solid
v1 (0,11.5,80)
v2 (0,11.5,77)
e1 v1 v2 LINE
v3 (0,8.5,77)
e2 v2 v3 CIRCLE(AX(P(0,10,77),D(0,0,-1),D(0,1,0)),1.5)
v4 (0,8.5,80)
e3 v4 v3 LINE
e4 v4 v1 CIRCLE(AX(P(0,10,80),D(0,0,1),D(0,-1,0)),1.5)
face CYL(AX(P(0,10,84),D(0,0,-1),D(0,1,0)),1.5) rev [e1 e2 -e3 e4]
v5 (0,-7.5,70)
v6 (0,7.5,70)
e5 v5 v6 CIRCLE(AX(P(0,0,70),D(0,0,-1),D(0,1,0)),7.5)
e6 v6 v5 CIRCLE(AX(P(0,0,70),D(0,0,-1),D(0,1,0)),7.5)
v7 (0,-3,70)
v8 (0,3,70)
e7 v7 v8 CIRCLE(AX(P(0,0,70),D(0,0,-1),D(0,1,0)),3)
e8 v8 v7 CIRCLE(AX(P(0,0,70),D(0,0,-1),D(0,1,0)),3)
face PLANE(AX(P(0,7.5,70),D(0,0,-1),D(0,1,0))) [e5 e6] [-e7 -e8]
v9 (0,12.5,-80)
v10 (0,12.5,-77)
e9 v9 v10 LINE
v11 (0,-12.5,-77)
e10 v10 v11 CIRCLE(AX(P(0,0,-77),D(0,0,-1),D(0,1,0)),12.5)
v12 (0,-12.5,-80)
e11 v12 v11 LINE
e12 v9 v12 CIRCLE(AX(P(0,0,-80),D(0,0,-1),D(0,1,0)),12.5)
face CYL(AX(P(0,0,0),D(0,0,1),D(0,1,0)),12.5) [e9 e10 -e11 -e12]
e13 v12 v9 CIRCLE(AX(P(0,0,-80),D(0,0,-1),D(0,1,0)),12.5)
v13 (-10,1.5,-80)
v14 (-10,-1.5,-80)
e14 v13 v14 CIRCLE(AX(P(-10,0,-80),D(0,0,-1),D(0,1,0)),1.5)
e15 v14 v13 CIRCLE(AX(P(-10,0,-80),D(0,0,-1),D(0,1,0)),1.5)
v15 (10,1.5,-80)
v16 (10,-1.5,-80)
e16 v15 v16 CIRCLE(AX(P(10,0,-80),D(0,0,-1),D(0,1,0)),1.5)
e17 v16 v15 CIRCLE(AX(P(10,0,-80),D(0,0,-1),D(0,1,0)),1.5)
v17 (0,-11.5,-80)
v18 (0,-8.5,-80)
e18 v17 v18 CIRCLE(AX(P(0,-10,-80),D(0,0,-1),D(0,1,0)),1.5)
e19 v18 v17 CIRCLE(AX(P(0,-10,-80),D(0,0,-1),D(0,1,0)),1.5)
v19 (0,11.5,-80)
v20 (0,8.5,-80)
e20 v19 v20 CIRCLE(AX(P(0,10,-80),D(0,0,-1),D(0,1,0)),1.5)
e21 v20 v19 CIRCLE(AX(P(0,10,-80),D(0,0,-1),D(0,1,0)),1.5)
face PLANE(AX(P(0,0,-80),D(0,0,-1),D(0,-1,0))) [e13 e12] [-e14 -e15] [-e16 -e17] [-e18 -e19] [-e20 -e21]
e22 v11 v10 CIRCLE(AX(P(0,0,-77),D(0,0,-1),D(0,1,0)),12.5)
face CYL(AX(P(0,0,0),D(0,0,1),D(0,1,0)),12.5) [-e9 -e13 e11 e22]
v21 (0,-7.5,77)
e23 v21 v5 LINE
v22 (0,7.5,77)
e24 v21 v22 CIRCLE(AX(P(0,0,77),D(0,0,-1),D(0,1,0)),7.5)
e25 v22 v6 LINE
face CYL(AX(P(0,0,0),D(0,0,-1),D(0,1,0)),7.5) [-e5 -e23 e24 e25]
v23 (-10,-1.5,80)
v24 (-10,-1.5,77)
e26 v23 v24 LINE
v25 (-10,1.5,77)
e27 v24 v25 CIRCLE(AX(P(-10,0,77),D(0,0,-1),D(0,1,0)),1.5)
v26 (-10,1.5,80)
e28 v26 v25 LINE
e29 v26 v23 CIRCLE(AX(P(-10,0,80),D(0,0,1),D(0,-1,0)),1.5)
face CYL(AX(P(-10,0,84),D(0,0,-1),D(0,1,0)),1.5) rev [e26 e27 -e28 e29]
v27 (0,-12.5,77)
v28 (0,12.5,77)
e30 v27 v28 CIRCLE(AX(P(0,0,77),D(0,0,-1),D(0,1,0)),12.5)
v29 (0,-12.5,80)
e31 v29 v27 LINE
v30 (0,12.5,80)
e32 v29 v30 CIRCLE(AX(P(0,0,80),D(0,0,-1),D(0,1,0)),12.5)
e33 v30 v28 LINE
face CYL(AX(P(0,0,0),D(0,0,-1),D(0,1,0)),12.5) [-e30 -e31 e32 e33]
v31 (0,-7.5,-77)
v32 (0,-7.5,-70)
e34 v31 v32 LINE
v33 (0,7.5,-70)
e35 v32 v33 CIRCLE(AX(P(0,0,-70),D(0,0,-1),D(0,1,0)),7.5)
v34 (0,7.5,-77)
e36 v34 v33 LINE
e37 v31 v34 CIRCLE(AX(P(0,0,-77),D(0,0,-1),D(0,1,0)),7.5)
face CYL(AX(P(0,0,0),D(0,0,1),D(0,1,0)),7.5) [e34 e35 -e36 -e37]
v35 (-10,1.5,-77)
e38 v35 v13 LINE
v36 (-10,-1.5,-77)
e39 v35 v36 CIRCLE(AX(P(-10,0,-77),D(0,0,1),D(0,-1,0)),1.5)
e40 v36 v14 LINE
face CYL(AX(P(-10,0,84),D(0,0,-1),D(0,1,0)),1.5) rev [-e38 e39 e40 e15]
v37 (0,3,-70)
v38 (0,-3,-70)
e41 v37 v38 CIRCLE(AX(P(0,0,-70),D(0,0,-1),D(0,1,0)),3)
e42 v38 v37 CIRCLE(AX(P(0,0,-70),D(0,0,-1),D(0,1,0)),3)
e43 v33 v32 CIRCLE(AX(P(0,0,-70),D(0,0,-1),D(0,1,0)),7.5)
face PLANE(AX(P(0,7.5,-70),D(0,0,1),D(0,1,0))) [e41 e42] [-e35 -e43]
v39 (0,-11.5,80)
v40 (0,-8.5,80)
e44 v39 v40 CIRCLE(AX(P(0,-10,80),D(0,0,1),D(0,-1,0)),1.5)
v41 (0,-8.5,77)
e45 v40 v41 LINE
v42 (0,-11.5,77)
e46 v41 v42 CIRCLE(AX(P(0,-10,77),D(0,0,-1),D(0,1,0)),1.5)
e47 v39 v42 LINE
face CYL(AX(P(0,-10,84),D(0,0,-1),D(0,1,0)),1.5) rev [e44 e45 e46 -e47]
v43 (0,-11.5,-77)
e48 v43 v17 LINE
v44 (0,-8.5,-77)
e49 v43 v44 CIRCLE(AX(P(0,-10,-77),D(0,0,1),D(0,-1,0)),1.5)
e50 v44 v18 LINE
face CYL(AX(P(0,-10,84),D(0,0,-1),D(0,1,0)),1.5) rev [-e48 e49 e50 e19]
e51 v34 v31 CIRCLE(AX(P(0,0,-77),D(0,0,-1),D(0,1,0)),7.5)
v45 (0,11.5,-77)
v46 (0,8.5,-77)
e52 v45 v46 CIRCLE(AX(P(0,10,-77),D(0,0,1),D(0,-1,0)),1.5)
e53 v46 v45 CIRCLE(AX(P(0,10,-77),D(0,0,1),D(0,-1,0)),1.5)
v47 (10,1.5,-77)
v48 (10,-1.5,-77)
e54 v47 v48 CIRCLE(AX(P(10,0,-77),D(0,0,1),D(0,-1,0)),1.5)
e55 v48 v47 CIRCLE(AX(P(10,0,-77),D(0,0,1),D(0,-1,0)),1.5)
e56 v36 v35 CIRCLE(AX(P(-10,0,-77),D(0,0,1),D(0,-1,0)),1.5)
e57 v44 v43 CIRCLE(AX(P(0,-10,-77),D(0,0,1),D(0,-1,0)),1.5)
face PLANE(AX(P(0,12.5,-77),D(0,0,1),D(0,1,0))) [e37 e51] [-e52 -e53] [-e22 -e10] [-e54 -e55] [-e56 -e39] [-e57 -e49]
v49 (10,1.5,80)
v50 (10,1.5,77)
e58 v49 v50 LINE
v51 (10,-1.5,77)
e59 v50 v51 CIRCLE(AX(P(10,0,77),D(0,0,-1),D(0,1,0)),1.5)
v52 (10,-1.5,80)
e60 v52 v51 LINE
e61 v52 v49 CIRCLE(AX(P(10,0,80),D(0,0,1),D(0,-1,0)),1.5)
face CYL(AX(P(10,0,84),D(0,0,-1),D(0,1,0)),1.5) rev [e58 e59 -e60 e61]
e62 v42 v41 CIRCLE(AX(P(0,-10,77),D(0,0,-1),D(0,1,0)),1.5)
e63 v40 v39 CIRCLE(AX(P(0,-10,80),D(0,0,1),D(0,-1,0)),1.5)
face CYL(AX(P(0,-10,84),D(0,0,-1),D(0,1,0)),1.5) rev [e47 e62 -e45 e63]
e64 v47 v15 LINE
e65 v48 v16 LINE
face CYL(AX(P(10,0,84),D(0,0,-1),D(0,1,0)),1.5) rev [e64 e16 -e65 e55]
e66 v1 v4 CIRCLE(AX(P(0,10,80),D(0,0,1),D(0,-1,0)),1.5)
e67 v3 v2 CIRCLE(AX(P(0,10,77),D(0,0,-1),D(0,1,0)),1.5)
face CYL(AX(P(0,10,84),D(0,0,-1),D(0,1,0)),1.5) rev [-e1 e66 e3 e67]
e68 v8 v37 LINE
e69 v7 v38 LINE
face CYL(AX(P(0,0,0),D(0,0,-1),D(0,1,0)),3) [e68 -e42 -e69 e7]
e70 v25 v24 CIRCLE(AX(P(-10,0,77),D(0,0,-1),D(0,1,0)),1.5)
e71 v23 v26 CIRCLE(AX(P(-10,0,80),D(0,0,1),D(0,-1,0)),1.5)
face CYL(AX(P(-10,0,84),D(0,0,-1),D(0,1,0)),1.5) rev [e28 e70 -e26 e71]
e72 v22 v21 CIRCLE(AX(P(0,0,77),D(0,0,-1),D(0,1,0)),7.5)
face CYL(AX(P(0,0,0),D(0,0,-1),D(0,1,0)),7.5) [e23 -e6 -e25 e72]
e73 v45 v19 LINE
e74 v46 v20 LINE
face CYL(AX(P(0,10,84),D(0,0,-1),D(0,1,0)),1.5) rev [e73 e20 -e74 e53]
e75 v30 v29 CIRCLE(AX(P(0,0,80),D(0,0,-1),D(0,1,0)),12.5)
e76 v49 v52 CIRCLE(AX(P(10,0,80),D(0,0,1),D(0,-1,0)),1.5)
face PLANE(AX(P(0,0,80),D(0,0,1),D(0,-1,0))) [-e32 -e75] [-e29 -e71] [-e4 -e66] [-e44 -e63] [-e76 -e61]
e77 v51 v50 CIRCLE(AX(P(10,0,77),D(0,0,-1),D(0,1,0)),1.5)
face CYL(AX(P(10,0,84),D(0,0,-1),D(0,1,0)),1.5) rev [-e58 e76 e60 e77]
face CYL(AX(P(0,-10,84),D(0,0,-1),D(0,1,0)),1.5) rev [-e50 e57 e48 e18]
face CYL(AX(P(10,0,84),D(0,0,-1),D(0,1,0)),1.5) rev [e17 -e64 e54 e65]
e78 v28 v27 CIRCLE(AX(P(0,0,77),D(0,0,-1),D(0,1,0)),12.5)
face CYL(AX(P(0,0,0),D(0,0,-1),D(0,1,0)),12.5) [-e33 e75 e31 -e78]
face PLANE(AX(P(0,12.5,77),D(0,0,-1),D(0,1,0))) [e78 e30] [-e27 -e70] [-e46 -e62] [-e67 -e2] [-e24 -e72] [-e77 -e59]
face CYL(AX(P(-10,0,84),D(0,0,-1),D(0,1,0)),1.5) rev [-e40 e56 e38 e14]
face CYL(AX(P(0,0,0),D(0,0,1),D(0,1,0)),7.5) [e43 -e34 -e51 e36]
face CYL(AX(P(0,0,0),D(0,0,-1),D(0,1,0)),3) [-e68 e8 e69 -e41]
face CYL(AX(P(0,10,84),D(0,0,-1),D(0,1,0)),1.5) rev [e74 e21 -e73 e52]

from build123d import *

# Parameters (mm, degrees)
SKETCH5_R          = 1.5
CUT_EXTRUDE4_DEPTH = 164


with BuildPart() as part:
    # Sketch4 → Revolve2 (revolve)
    with BuildSketch(Plane(origin=(0, 0, 0), x_dir=(0, 0, -1), z_dir=(1, 0, 0))):
        Polygon((-80, 0), (-80, 12.5), (-77, 12.5), (-77, 7.5), (-70, 7.5), (-70, 3), (0, 3), (0, 0), align=None)
    revolve2 = revolve(axis=Axis((0, 0, 0), (0, 0, 1)))

    # Mirror1: Revolve2 across plane
    add(revolve2.mirror(Plane(origin=(0, 0, 0), x_dir=(1, 0, 0), z_dir=(0, 0, -1))))

    # Sketch5 → Cut-Extrude4 (cut)
    with BuildSketch(Plane(origin=(0, 0, -80), x_dir=(-1, 0, 0), z_dir=(0, 0, -1))):
        with Locations(Location((10, 0, 0), (0, 0, 90))):
            Circle(SKETCH5_R)
        with Locations(Location((0, -10, 0), (0, 0, 90))):
            Circle(SKETCH5_R)
        with Locations(Location((-10, 0, 0), (0, 0, 90))):
            Circle(SKETCH5_R)
        with Locations(Location((0, 10, 0), (0, 0, 90))):
            Circle(SKETCH5_R)
    extrude(amount=-CUT_EXTRUDE4_DEPTH, mode=Mode.SUBTRACT)


solid = part.part
